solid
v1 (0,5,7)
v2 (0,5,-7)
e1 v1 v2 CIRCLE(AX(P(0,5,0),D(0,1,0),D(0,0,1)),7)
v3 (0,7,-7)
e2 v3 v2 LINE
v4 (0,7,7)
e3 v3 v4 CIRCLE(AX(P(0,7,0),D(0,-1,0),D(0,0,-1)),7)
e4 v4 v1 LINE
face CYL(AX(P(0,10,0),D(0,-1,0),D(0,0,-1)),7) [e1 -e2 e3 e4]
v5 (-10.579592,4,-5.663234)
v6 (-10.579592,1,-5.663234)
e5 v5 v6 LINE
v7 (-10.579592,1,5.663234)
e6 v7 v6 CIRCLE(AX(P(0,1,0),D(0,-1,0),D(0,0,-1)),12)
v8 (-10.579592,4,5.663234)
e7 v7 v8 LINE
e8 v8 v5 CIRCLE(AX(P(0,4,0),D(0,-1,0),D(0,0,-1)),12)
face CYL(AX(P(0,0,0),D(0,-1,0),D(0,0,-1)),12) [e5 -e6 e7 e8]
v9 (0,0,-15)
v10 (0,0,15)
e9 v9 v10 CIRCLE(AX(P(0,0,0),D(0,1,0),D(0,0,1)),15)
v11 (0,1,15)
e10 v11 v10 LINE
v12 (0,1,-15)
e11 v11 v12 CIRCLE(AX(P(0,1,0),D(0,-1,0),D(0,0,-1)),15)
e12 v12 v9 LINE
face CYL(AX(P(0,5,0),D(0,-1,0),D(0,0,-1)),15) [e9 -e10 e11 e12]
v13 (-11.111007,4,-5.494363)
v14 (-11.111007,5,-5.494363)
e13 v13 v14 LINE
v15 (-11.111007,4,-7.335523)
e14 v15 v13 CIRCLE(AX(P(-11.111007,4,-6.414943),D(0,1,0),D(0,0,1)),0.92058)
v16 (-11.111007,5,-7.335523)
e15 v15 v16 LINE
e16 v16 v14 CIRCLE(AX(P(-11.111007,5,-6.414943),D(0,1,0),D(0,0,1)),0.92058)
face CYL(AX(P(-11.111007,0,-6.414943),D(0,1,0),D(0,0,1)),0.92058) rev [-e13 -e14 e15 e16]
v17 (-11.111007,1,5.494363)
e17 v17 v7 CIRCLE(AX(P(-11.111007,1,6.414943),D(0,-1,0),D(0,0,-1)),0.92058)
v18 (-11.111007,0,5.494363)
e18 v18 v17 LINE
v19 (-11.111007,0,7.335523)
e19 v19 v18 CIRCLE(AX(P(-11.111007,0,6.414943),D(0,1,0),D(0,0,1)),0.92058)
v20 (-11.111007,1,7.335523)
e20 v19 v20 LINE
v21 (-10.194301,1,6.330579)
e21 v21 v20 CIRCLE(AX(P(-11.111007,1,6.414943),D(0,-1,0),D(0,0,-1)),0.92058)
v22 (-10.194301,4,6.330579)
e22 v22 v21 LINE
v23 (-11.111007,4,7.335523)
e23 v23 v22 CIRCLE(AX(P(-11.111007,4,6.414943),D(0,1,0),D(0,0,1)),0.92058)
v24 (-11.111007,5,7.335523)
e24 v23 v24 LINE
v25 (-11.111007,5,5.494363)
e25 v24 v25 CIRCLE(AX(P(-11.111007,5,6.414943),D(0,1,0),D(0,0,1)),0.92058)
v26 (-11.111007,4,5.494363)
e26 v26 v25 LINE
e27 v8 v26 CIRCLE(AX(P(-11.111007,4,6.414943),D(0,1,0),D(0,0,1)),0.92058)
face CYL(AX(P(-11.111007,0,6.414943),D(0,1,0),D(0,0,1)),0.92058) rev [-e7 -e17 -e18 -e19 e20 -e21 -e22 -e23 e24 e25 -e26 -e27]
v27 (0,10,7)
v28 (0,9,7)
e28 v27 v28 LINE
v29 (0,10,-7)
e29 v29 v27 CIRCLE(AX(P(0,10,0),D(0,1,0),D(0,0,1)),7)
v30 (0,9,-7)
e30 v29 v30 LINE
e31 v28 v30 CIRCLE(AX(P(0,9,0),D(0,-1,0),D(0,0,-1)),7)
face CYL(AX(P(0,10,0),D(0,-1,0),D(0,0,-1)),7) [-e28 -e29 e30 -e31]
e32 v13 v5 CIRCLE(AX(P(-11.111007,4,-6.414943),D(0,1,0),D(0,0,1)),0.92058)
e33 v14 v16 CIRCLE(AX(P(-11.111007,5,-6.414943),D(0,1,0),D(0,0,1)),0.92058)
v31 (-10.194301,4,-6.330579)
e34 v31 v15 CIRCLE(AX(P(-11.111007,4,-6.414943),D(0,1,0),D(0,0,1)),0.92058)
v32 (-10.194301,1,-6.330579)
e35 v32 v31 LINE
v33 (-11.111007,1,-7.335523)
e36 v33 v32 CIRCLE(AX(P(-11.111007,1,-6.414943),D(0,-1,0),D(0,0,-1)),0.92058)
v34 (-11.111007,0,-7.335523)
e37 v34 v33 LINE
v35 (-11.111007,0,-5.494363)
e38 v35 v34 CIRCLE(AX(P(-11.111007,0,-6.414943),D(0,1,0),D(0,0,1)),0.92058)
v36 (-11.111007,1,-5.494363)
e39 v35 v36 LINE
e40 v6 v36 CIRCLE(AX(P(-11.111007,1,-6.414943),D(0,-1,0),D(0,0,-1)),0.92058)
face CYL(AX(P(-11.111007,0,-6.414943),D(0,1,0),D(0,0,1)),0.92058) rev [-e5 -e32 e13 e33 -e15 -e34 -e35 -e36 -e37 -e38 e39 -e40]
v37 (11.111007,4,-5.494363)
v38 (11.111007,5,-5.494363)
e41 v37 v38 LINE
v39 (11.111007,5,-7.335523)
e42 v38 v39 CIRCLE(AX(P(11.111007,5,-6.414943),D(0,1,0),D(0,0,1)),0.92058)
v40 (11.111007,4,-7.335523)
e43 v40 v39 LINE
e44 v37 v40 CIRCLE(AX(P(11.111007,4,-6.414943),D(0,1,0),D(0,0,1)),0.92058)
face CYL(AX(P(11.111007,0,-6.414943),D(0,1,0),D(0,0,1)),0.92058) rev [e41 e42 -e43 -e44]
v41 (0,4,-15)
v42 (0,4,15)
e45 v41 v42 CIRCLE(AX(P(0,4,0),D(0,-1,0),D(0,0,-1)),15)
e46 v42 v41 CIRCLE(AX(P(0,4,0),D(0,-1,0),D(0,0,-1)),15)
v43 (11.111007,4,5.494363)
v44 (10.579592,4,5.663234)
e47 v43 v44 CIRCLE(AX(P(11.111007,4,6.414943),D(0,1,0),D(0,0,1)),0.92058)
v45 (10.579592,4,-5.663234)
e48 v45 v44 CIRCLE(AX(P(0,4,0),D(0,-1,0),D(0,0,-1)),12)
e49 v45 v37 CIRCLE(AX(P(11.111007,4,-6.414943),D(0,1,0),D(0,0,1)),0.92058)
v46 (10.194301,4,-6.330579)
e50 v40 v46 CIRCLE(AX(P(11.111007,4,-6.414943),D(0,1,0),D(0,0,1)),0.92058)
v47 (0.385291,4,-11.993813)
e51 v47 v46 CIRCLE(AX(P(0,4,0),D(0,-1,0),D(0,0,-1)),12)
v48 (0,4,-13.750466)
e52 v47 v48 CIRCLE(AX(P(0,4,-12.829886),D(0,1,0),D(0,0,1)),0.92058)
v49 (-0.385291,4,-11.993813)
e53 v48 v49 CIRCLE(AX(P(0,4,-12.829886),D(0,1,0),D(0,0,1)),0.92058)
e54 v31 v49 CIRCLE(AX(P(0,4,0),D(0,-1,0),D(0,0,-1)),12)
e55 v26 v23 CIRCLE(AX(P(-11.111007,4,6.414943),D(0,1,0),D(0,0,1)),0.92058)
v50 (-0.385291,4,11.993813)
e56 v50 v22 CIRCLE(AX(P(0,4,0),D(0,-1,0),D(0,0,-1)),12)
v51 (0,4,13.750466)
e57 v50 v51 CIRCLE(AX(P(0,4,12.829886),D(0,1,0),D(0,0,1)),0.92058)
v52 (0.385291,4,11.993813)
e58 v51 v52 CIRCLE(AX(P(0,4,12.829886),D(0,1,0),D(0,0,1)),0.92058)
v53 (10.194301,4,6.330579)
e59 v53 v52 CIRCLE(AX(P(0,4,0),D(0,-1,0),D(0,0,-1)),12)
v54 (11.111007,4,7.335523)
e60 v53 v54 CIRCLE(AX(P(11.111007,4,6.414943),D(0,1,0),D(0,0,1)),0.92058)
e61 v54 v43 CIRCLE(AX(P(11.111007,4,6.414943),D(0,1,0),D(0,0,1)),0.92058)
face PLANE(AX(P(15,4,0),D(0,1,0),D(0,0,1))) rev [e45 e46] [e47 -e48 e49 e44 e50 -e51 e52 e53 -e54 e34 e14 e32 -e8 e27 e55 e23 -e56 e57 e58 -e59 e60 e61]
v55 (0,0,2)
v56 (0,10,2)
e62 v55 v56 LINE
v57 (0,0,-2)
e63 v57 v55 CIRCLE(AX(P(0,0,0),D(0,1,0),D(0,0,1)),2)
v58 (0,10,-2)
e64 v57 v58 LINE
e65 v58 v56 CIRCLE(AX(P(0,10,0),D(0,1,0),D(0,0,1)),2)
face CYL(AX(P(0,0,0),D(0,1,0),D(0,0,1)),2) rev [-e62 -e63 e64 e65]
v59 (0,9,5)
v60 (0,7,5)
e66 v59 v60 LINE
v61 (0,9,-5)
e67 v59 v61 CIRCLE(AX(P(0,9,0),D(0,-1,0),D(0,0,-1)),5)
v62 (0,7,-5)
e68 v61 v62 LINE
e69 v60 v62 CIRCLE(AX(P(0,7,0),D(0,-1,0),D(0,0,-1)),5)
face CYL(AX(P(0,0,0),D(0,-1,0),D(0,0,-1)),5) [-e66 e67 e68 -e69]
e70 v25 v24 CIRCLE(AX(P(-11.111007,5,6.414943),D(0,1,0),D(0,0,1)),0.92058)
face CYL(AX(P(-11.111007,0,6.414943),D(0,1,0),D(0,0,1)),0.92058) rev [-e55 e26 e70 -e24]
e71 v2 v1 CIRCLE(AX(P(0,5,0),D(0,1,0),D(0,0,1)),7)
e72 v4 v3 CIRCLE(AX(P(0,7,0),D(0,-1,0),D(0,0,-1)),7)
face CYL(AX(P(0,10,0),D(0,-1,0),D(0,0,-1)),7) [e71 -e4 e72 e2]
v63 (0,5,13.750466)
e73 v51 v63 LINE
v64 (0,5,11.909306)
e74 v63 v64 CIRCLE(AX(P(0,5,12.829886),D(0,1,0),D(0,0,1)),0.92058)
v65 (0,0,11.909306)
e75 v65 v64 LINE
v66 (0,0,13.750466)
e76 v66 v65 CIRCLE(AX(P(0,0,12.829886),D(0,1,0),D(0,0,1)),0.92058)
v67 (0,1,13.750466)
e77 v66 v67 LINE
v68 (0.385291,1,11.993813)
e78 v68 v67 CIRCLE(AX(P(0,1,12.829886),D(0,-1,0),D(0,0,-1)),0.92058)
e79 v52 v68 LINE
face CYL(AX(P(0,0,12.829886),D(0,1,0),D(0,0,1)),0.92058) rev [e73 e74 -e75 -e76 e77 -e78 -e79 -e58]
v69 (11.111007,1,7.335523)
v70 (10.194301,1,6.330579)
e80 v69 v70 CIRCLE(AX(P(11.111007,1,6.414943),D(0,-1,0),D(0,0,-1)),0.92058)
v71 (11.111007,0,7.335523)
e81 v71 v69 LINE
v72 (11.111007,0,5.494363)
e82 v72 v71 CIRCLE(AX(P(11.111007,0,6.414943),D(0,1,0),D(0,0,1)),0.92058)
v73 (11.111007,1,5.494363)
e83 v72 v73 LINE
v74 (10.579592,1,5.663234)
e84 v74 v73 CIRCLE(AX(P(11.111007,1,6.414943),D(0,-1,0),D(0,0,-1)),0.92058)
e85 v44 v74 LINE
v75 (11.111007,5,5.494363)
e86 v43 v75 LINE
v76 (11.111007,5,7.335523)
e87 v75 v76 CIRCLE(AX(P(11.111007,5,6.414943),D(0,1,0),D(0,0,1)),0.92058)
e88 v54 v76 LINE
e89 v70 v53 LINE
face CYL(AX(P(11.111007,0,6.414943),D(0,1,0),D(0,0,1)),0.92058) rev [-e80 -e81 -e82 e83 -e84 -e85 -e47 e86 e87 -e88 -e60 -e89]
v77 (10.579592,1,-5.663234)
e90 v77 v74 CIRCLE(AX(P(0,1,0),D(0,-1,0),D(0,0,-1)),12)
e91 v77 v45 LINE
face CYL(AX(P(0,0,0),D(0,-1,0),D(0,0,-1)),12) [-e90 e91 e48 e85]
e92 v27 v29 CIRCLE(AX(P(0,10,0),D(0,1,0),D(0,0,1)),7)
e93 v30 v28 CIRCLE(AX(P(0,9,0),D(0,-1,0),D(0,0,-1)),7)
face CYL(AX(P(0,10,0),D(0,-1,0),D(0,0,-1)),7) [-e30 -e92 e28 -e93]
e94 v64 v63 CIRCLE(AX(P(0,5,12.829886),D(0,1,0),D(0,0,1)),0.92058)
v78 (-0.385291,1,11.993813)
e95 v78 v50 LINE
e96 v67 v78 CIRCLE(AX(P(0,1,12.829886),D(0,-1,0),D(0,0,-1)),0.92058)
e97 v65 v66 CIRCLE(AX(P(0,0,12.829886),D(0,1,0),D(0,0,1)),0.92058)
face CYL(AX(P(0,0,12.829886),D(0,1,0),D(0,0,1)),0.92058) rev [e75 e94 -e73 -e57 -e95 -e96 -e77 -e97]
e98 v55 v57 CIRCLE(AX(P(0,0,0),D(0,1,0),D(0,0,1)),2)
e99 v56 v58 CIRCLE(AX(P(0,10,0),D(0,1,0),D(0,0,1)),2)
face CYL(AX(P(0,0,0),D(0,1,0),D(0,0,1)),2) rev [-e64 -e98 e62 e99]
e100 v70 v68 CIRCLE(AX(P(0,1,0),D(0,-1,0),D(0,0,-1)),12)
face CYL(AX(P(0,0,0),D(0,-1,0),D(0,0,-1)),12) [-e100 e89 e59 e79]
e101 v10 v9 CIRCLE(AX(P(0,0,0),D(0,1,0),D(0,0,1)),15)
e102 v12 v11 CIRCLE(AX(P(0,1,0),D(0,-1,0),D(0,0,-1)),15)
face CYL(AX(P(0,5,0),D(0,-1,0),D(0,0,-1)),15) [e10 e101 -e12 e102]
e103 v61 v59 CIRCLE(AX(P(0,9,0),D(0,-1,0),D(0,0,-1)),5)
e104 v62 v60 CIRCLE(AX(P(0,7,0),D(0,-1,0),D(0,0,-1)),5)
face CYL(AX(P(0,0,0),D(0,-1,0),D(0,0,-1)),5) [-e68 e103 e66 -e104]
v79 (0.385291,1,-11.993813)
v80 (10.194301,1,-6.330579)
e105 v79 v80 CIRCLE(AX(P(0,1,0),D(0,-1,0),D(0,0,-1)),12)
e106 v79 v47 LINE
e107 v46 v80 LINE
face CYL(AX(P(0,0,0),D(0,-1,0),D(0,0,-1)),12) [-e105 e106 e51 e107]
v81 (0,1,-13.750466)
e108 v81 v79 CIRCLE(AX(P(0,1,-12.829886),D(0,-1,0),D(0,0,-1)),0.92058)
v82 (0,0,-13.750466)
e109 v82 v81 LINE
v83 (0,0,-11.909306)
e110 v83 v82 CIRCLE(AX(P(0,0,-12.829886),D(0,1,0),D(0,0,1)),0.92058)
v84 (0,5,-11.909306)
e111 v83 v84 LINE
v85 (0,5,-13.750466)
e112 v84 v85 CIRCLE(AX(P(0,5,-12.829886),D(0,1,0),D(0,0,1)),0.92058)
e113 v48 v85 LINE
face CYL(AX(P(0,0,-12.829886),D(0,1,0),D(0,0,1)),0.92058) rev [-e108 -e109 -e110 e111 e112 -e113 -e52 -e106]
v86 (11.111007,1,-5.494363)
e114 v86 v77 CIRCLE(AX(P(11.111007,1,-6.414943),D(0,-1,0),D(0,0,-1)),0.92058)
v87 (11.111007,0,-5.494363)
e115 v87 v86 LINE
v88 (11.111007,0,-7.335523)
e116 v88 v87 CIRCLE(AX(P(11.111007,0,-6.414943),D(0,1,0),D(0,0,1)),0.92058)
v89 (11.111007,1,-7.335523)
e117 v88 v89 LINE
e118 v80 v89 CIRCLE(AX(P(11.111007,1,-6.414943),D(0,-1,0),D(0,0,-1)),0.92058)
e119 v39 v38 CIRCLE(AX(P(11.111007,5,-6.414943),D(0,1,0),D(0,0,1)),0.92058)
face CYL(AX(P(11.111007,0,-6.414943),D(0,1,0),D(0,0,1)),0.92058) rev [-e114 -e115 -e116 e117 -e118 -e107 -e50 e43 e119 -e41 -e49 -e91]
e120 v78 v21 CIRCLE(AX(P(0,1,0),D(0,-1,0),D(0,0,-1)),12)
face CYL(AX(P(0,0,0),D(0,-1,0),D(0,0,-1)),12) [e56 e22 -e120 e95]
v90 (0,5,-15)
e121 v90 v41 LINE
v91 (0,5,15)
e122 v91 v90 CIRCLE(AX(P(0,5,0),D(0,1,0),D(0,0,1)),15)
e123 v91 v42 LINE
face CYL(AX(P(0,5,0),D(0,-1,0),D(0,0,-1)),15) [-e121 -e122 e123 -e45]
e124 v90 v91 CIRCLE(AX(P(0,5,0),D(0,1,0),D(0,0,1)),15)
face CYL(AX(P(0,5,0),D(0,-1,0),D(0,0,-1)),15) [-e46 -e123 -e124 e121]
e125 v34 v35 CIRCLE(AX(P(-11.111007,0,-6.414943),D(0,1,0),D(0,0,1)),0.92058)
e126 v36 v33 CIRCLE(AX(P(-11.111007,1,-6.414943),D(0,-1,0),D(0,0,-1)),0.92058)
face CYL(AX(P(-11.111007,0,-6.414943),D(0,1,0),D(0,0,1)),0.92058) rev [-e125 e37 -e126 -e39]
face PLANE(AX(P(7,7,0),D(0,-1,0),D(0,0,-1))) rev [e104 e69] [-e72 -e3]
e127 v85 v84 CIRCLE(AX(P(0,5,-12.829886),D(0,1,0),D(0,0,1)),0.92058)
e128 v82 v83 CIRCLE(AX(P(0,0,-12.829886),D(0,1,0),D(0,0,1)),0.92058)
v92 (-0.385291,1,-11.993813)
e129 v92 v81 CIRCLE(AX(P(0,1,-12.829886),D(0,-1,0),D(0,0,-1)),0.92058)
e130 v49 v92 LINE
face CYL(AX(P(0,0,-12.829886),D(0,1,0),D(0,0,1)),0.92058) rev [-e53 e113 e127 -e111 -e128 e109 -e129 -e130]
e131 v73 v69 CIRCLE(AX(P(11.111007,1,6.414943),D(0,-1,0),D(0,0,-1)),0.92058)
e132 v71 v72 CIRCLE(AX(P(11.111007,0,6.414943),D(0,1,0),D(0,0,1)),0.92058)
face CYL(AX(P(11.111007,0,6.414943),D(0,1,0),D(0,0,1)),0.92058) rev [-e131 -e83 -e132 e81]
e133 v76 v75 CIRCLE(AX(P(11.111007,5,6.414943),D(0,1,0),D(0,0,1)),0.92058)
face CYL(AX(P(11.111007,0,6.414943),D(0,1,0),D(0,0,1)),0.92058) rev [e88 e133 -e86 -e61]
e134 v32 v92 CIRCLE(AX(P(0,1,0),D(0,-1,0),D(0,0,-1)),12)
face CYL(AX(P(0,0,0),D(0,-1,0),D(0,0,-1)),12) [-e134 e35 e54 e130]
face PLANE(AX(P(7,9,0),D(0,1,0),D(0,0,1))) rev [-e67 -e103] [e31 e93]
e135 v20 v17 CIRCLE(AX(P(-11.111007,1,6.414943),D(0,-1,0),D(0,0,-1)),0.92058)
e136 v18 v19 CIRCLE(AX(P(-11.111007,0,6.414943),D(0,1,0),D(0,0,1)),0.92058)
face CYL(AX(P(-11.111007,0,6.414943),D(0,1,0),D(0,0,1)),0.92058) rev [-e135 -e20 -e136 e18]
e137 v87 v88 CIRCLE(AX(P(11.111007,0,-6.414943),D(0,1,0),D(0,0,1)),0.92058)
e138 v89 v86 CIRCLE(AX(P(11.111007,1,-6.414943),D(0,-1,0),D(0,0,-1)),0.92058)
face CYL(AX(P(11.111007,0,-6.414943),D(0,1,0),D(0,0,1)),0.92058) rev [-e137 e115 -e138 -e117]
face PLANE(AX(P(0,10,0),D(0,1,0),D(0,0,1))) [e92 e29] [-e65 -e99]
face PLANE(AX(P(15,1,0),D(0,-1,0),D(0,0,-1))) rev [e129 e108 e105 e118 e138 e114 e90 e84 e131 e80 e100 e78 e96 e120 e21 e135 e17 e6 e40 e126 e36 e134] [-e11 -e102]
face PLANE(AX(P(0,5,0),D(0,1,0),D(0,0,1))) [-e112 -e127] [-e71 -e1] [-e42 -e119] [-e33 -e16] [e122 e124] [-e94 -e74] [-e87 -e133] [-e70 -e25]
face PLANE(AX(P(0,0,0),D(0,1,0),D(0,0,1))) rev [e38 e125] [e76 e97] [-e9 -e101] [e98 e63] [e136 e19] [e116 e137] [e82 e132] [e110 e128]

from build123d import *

# Parameters (mm, degrees)
SKETCH1_R               = 15
BOSS_EXTRUDE1_DEPTH     = 5
SKETCH2_W               = 3
SKETCH2_H               = 3
SKETCH3_R               = 7
BOSS_EXTRUDE2_DEPTH     = 5
SKETCH4_W               = 2
SKETCH4_H               = 2
SKETCH5_R               = 2
CUT_EXTRUDE1_DEPTH      = 24.452078799
CUT_EXTRUDE2_DEPTH      = 22.794494718
CUT_EXTRUDE2_DEPTH_BACK = 22.794494718
SKETCH6_R               = 0.920579976


with BuildPart() as part:
    # Sketch1 → Boss-Extrude1 (new body)
    with BuildSketch(Plane(origin=(0, 0, 0), x_dir=(1, 0, 0), z_dir=(0, 1, 0))):
        with Locations(Location((0, 0, 0), (0, 0, 270))):
            Circle(SKETCH1_R)
    extrude(amount=BOSS_EXTRUDE1_DEPTH)

    # Sketch2 → Cut-Revolve1 (revolve, cut)
    with BuildSketch(Plane.XY, mode=Mode.PRIVATE) as cut_revolve1_sk:
        with Locations((13.5, 2.5)):
            Rectangle(SKETCH2_W, SKETCH2_H)
    revolve(cut_revolve1_sk.sketch.rotate(Axis((0, 0, 0), (0, 1, 0)), 90), axis=Axis((0, 0, 0), (0, 1, 0)), mode=Mode.SUBTRACT)

    # Sketch3 → Boss-Extrude2 (add)
    with BuildSketch(Plane(origin=(0, 5, 0), x_dir=(1, 0, 0), z_dir=(0, 1, 0))):
        with Locations(Location((0, 0, 0), (0, 0, 270))):
            Circle(SKETCH3_R)
    extrude(amount=BOSS_EXTRUDE2_DEPTH)

    # Sketch4 → Cut-Revolve2 (revolve, cut)
    with BuildSketch(Plane.XY, mode=Mode.PRIVATE) as cut_revolve2_sk:
        with Locations((6, 8)):
            Rectangle(SKETCH4_W, SKETCH4_H)
    revolve(cut_revolve2_sk.sketch.rotate(Axis((0, 0, 0), (0, 1, 0)), 90), axis=Axis((0, 0, 0), (0, 1, 0)), mode=Mode.SUBTRACT)

    # Sketch5 → Cut-Extrude1 (cut, through all)
    with BuildSketch(Plane(origin=(0, 10, 0), x_dir=(1, 0, 0), z_dir=(0, 1, 0))):
        with Locations(Location((0, 0, 0), (0, 0, 270))):
            Circle(SKETCH5_R)
    extrude(amount=-CUT_EXTRUDE1_DEPTH, mode=Mode.SUBTRACT)

    # Sketch6 → Cut-Extrude2 (cut, two sides: drawn at the far end of the back side and taken through both)
    with BuildSketch(Plane(origin=(0, 5, 0), x_dir=(1, 0, 0), z_dir=(0, 1, 0)).offset(-CUT_EXTRUDE2_DEPTH_BACK)):
        with Locations(Location((0, 12.829886063, 0), (0, 0, 270))):
            Circle(SKETCH6_R)
        with Locations(Location((11.111007258, 6.414943031, 0), (0, 0, 270))):
            Circle(SKETCH6_R)
        with Locations(Location((11.111007258, -6.414943031, 0), (0, 0, 270))):
            Circle(SKETCH6_R)
        with Locations(Location((0, -12.829886063, 0), (0, 0, 270))):
            Circle(SKETCH6_R)
        with Locations(Location((-11.111007258, -6.414943031, 0), (0, 0, 270))):
            Circle(SKETCH6_R)
        with Locations(Location((-11.111007258, 6.414943031, 0), (0, 0, 270))):
            Circle(SKETCH6_R)
    extrude(amount=CUT_EXTRUDE2_DEPTH + CUT_EXTRUDE2_DEPTH_BACK, mode=Mode.SUBTRACT)


solid = part.part
